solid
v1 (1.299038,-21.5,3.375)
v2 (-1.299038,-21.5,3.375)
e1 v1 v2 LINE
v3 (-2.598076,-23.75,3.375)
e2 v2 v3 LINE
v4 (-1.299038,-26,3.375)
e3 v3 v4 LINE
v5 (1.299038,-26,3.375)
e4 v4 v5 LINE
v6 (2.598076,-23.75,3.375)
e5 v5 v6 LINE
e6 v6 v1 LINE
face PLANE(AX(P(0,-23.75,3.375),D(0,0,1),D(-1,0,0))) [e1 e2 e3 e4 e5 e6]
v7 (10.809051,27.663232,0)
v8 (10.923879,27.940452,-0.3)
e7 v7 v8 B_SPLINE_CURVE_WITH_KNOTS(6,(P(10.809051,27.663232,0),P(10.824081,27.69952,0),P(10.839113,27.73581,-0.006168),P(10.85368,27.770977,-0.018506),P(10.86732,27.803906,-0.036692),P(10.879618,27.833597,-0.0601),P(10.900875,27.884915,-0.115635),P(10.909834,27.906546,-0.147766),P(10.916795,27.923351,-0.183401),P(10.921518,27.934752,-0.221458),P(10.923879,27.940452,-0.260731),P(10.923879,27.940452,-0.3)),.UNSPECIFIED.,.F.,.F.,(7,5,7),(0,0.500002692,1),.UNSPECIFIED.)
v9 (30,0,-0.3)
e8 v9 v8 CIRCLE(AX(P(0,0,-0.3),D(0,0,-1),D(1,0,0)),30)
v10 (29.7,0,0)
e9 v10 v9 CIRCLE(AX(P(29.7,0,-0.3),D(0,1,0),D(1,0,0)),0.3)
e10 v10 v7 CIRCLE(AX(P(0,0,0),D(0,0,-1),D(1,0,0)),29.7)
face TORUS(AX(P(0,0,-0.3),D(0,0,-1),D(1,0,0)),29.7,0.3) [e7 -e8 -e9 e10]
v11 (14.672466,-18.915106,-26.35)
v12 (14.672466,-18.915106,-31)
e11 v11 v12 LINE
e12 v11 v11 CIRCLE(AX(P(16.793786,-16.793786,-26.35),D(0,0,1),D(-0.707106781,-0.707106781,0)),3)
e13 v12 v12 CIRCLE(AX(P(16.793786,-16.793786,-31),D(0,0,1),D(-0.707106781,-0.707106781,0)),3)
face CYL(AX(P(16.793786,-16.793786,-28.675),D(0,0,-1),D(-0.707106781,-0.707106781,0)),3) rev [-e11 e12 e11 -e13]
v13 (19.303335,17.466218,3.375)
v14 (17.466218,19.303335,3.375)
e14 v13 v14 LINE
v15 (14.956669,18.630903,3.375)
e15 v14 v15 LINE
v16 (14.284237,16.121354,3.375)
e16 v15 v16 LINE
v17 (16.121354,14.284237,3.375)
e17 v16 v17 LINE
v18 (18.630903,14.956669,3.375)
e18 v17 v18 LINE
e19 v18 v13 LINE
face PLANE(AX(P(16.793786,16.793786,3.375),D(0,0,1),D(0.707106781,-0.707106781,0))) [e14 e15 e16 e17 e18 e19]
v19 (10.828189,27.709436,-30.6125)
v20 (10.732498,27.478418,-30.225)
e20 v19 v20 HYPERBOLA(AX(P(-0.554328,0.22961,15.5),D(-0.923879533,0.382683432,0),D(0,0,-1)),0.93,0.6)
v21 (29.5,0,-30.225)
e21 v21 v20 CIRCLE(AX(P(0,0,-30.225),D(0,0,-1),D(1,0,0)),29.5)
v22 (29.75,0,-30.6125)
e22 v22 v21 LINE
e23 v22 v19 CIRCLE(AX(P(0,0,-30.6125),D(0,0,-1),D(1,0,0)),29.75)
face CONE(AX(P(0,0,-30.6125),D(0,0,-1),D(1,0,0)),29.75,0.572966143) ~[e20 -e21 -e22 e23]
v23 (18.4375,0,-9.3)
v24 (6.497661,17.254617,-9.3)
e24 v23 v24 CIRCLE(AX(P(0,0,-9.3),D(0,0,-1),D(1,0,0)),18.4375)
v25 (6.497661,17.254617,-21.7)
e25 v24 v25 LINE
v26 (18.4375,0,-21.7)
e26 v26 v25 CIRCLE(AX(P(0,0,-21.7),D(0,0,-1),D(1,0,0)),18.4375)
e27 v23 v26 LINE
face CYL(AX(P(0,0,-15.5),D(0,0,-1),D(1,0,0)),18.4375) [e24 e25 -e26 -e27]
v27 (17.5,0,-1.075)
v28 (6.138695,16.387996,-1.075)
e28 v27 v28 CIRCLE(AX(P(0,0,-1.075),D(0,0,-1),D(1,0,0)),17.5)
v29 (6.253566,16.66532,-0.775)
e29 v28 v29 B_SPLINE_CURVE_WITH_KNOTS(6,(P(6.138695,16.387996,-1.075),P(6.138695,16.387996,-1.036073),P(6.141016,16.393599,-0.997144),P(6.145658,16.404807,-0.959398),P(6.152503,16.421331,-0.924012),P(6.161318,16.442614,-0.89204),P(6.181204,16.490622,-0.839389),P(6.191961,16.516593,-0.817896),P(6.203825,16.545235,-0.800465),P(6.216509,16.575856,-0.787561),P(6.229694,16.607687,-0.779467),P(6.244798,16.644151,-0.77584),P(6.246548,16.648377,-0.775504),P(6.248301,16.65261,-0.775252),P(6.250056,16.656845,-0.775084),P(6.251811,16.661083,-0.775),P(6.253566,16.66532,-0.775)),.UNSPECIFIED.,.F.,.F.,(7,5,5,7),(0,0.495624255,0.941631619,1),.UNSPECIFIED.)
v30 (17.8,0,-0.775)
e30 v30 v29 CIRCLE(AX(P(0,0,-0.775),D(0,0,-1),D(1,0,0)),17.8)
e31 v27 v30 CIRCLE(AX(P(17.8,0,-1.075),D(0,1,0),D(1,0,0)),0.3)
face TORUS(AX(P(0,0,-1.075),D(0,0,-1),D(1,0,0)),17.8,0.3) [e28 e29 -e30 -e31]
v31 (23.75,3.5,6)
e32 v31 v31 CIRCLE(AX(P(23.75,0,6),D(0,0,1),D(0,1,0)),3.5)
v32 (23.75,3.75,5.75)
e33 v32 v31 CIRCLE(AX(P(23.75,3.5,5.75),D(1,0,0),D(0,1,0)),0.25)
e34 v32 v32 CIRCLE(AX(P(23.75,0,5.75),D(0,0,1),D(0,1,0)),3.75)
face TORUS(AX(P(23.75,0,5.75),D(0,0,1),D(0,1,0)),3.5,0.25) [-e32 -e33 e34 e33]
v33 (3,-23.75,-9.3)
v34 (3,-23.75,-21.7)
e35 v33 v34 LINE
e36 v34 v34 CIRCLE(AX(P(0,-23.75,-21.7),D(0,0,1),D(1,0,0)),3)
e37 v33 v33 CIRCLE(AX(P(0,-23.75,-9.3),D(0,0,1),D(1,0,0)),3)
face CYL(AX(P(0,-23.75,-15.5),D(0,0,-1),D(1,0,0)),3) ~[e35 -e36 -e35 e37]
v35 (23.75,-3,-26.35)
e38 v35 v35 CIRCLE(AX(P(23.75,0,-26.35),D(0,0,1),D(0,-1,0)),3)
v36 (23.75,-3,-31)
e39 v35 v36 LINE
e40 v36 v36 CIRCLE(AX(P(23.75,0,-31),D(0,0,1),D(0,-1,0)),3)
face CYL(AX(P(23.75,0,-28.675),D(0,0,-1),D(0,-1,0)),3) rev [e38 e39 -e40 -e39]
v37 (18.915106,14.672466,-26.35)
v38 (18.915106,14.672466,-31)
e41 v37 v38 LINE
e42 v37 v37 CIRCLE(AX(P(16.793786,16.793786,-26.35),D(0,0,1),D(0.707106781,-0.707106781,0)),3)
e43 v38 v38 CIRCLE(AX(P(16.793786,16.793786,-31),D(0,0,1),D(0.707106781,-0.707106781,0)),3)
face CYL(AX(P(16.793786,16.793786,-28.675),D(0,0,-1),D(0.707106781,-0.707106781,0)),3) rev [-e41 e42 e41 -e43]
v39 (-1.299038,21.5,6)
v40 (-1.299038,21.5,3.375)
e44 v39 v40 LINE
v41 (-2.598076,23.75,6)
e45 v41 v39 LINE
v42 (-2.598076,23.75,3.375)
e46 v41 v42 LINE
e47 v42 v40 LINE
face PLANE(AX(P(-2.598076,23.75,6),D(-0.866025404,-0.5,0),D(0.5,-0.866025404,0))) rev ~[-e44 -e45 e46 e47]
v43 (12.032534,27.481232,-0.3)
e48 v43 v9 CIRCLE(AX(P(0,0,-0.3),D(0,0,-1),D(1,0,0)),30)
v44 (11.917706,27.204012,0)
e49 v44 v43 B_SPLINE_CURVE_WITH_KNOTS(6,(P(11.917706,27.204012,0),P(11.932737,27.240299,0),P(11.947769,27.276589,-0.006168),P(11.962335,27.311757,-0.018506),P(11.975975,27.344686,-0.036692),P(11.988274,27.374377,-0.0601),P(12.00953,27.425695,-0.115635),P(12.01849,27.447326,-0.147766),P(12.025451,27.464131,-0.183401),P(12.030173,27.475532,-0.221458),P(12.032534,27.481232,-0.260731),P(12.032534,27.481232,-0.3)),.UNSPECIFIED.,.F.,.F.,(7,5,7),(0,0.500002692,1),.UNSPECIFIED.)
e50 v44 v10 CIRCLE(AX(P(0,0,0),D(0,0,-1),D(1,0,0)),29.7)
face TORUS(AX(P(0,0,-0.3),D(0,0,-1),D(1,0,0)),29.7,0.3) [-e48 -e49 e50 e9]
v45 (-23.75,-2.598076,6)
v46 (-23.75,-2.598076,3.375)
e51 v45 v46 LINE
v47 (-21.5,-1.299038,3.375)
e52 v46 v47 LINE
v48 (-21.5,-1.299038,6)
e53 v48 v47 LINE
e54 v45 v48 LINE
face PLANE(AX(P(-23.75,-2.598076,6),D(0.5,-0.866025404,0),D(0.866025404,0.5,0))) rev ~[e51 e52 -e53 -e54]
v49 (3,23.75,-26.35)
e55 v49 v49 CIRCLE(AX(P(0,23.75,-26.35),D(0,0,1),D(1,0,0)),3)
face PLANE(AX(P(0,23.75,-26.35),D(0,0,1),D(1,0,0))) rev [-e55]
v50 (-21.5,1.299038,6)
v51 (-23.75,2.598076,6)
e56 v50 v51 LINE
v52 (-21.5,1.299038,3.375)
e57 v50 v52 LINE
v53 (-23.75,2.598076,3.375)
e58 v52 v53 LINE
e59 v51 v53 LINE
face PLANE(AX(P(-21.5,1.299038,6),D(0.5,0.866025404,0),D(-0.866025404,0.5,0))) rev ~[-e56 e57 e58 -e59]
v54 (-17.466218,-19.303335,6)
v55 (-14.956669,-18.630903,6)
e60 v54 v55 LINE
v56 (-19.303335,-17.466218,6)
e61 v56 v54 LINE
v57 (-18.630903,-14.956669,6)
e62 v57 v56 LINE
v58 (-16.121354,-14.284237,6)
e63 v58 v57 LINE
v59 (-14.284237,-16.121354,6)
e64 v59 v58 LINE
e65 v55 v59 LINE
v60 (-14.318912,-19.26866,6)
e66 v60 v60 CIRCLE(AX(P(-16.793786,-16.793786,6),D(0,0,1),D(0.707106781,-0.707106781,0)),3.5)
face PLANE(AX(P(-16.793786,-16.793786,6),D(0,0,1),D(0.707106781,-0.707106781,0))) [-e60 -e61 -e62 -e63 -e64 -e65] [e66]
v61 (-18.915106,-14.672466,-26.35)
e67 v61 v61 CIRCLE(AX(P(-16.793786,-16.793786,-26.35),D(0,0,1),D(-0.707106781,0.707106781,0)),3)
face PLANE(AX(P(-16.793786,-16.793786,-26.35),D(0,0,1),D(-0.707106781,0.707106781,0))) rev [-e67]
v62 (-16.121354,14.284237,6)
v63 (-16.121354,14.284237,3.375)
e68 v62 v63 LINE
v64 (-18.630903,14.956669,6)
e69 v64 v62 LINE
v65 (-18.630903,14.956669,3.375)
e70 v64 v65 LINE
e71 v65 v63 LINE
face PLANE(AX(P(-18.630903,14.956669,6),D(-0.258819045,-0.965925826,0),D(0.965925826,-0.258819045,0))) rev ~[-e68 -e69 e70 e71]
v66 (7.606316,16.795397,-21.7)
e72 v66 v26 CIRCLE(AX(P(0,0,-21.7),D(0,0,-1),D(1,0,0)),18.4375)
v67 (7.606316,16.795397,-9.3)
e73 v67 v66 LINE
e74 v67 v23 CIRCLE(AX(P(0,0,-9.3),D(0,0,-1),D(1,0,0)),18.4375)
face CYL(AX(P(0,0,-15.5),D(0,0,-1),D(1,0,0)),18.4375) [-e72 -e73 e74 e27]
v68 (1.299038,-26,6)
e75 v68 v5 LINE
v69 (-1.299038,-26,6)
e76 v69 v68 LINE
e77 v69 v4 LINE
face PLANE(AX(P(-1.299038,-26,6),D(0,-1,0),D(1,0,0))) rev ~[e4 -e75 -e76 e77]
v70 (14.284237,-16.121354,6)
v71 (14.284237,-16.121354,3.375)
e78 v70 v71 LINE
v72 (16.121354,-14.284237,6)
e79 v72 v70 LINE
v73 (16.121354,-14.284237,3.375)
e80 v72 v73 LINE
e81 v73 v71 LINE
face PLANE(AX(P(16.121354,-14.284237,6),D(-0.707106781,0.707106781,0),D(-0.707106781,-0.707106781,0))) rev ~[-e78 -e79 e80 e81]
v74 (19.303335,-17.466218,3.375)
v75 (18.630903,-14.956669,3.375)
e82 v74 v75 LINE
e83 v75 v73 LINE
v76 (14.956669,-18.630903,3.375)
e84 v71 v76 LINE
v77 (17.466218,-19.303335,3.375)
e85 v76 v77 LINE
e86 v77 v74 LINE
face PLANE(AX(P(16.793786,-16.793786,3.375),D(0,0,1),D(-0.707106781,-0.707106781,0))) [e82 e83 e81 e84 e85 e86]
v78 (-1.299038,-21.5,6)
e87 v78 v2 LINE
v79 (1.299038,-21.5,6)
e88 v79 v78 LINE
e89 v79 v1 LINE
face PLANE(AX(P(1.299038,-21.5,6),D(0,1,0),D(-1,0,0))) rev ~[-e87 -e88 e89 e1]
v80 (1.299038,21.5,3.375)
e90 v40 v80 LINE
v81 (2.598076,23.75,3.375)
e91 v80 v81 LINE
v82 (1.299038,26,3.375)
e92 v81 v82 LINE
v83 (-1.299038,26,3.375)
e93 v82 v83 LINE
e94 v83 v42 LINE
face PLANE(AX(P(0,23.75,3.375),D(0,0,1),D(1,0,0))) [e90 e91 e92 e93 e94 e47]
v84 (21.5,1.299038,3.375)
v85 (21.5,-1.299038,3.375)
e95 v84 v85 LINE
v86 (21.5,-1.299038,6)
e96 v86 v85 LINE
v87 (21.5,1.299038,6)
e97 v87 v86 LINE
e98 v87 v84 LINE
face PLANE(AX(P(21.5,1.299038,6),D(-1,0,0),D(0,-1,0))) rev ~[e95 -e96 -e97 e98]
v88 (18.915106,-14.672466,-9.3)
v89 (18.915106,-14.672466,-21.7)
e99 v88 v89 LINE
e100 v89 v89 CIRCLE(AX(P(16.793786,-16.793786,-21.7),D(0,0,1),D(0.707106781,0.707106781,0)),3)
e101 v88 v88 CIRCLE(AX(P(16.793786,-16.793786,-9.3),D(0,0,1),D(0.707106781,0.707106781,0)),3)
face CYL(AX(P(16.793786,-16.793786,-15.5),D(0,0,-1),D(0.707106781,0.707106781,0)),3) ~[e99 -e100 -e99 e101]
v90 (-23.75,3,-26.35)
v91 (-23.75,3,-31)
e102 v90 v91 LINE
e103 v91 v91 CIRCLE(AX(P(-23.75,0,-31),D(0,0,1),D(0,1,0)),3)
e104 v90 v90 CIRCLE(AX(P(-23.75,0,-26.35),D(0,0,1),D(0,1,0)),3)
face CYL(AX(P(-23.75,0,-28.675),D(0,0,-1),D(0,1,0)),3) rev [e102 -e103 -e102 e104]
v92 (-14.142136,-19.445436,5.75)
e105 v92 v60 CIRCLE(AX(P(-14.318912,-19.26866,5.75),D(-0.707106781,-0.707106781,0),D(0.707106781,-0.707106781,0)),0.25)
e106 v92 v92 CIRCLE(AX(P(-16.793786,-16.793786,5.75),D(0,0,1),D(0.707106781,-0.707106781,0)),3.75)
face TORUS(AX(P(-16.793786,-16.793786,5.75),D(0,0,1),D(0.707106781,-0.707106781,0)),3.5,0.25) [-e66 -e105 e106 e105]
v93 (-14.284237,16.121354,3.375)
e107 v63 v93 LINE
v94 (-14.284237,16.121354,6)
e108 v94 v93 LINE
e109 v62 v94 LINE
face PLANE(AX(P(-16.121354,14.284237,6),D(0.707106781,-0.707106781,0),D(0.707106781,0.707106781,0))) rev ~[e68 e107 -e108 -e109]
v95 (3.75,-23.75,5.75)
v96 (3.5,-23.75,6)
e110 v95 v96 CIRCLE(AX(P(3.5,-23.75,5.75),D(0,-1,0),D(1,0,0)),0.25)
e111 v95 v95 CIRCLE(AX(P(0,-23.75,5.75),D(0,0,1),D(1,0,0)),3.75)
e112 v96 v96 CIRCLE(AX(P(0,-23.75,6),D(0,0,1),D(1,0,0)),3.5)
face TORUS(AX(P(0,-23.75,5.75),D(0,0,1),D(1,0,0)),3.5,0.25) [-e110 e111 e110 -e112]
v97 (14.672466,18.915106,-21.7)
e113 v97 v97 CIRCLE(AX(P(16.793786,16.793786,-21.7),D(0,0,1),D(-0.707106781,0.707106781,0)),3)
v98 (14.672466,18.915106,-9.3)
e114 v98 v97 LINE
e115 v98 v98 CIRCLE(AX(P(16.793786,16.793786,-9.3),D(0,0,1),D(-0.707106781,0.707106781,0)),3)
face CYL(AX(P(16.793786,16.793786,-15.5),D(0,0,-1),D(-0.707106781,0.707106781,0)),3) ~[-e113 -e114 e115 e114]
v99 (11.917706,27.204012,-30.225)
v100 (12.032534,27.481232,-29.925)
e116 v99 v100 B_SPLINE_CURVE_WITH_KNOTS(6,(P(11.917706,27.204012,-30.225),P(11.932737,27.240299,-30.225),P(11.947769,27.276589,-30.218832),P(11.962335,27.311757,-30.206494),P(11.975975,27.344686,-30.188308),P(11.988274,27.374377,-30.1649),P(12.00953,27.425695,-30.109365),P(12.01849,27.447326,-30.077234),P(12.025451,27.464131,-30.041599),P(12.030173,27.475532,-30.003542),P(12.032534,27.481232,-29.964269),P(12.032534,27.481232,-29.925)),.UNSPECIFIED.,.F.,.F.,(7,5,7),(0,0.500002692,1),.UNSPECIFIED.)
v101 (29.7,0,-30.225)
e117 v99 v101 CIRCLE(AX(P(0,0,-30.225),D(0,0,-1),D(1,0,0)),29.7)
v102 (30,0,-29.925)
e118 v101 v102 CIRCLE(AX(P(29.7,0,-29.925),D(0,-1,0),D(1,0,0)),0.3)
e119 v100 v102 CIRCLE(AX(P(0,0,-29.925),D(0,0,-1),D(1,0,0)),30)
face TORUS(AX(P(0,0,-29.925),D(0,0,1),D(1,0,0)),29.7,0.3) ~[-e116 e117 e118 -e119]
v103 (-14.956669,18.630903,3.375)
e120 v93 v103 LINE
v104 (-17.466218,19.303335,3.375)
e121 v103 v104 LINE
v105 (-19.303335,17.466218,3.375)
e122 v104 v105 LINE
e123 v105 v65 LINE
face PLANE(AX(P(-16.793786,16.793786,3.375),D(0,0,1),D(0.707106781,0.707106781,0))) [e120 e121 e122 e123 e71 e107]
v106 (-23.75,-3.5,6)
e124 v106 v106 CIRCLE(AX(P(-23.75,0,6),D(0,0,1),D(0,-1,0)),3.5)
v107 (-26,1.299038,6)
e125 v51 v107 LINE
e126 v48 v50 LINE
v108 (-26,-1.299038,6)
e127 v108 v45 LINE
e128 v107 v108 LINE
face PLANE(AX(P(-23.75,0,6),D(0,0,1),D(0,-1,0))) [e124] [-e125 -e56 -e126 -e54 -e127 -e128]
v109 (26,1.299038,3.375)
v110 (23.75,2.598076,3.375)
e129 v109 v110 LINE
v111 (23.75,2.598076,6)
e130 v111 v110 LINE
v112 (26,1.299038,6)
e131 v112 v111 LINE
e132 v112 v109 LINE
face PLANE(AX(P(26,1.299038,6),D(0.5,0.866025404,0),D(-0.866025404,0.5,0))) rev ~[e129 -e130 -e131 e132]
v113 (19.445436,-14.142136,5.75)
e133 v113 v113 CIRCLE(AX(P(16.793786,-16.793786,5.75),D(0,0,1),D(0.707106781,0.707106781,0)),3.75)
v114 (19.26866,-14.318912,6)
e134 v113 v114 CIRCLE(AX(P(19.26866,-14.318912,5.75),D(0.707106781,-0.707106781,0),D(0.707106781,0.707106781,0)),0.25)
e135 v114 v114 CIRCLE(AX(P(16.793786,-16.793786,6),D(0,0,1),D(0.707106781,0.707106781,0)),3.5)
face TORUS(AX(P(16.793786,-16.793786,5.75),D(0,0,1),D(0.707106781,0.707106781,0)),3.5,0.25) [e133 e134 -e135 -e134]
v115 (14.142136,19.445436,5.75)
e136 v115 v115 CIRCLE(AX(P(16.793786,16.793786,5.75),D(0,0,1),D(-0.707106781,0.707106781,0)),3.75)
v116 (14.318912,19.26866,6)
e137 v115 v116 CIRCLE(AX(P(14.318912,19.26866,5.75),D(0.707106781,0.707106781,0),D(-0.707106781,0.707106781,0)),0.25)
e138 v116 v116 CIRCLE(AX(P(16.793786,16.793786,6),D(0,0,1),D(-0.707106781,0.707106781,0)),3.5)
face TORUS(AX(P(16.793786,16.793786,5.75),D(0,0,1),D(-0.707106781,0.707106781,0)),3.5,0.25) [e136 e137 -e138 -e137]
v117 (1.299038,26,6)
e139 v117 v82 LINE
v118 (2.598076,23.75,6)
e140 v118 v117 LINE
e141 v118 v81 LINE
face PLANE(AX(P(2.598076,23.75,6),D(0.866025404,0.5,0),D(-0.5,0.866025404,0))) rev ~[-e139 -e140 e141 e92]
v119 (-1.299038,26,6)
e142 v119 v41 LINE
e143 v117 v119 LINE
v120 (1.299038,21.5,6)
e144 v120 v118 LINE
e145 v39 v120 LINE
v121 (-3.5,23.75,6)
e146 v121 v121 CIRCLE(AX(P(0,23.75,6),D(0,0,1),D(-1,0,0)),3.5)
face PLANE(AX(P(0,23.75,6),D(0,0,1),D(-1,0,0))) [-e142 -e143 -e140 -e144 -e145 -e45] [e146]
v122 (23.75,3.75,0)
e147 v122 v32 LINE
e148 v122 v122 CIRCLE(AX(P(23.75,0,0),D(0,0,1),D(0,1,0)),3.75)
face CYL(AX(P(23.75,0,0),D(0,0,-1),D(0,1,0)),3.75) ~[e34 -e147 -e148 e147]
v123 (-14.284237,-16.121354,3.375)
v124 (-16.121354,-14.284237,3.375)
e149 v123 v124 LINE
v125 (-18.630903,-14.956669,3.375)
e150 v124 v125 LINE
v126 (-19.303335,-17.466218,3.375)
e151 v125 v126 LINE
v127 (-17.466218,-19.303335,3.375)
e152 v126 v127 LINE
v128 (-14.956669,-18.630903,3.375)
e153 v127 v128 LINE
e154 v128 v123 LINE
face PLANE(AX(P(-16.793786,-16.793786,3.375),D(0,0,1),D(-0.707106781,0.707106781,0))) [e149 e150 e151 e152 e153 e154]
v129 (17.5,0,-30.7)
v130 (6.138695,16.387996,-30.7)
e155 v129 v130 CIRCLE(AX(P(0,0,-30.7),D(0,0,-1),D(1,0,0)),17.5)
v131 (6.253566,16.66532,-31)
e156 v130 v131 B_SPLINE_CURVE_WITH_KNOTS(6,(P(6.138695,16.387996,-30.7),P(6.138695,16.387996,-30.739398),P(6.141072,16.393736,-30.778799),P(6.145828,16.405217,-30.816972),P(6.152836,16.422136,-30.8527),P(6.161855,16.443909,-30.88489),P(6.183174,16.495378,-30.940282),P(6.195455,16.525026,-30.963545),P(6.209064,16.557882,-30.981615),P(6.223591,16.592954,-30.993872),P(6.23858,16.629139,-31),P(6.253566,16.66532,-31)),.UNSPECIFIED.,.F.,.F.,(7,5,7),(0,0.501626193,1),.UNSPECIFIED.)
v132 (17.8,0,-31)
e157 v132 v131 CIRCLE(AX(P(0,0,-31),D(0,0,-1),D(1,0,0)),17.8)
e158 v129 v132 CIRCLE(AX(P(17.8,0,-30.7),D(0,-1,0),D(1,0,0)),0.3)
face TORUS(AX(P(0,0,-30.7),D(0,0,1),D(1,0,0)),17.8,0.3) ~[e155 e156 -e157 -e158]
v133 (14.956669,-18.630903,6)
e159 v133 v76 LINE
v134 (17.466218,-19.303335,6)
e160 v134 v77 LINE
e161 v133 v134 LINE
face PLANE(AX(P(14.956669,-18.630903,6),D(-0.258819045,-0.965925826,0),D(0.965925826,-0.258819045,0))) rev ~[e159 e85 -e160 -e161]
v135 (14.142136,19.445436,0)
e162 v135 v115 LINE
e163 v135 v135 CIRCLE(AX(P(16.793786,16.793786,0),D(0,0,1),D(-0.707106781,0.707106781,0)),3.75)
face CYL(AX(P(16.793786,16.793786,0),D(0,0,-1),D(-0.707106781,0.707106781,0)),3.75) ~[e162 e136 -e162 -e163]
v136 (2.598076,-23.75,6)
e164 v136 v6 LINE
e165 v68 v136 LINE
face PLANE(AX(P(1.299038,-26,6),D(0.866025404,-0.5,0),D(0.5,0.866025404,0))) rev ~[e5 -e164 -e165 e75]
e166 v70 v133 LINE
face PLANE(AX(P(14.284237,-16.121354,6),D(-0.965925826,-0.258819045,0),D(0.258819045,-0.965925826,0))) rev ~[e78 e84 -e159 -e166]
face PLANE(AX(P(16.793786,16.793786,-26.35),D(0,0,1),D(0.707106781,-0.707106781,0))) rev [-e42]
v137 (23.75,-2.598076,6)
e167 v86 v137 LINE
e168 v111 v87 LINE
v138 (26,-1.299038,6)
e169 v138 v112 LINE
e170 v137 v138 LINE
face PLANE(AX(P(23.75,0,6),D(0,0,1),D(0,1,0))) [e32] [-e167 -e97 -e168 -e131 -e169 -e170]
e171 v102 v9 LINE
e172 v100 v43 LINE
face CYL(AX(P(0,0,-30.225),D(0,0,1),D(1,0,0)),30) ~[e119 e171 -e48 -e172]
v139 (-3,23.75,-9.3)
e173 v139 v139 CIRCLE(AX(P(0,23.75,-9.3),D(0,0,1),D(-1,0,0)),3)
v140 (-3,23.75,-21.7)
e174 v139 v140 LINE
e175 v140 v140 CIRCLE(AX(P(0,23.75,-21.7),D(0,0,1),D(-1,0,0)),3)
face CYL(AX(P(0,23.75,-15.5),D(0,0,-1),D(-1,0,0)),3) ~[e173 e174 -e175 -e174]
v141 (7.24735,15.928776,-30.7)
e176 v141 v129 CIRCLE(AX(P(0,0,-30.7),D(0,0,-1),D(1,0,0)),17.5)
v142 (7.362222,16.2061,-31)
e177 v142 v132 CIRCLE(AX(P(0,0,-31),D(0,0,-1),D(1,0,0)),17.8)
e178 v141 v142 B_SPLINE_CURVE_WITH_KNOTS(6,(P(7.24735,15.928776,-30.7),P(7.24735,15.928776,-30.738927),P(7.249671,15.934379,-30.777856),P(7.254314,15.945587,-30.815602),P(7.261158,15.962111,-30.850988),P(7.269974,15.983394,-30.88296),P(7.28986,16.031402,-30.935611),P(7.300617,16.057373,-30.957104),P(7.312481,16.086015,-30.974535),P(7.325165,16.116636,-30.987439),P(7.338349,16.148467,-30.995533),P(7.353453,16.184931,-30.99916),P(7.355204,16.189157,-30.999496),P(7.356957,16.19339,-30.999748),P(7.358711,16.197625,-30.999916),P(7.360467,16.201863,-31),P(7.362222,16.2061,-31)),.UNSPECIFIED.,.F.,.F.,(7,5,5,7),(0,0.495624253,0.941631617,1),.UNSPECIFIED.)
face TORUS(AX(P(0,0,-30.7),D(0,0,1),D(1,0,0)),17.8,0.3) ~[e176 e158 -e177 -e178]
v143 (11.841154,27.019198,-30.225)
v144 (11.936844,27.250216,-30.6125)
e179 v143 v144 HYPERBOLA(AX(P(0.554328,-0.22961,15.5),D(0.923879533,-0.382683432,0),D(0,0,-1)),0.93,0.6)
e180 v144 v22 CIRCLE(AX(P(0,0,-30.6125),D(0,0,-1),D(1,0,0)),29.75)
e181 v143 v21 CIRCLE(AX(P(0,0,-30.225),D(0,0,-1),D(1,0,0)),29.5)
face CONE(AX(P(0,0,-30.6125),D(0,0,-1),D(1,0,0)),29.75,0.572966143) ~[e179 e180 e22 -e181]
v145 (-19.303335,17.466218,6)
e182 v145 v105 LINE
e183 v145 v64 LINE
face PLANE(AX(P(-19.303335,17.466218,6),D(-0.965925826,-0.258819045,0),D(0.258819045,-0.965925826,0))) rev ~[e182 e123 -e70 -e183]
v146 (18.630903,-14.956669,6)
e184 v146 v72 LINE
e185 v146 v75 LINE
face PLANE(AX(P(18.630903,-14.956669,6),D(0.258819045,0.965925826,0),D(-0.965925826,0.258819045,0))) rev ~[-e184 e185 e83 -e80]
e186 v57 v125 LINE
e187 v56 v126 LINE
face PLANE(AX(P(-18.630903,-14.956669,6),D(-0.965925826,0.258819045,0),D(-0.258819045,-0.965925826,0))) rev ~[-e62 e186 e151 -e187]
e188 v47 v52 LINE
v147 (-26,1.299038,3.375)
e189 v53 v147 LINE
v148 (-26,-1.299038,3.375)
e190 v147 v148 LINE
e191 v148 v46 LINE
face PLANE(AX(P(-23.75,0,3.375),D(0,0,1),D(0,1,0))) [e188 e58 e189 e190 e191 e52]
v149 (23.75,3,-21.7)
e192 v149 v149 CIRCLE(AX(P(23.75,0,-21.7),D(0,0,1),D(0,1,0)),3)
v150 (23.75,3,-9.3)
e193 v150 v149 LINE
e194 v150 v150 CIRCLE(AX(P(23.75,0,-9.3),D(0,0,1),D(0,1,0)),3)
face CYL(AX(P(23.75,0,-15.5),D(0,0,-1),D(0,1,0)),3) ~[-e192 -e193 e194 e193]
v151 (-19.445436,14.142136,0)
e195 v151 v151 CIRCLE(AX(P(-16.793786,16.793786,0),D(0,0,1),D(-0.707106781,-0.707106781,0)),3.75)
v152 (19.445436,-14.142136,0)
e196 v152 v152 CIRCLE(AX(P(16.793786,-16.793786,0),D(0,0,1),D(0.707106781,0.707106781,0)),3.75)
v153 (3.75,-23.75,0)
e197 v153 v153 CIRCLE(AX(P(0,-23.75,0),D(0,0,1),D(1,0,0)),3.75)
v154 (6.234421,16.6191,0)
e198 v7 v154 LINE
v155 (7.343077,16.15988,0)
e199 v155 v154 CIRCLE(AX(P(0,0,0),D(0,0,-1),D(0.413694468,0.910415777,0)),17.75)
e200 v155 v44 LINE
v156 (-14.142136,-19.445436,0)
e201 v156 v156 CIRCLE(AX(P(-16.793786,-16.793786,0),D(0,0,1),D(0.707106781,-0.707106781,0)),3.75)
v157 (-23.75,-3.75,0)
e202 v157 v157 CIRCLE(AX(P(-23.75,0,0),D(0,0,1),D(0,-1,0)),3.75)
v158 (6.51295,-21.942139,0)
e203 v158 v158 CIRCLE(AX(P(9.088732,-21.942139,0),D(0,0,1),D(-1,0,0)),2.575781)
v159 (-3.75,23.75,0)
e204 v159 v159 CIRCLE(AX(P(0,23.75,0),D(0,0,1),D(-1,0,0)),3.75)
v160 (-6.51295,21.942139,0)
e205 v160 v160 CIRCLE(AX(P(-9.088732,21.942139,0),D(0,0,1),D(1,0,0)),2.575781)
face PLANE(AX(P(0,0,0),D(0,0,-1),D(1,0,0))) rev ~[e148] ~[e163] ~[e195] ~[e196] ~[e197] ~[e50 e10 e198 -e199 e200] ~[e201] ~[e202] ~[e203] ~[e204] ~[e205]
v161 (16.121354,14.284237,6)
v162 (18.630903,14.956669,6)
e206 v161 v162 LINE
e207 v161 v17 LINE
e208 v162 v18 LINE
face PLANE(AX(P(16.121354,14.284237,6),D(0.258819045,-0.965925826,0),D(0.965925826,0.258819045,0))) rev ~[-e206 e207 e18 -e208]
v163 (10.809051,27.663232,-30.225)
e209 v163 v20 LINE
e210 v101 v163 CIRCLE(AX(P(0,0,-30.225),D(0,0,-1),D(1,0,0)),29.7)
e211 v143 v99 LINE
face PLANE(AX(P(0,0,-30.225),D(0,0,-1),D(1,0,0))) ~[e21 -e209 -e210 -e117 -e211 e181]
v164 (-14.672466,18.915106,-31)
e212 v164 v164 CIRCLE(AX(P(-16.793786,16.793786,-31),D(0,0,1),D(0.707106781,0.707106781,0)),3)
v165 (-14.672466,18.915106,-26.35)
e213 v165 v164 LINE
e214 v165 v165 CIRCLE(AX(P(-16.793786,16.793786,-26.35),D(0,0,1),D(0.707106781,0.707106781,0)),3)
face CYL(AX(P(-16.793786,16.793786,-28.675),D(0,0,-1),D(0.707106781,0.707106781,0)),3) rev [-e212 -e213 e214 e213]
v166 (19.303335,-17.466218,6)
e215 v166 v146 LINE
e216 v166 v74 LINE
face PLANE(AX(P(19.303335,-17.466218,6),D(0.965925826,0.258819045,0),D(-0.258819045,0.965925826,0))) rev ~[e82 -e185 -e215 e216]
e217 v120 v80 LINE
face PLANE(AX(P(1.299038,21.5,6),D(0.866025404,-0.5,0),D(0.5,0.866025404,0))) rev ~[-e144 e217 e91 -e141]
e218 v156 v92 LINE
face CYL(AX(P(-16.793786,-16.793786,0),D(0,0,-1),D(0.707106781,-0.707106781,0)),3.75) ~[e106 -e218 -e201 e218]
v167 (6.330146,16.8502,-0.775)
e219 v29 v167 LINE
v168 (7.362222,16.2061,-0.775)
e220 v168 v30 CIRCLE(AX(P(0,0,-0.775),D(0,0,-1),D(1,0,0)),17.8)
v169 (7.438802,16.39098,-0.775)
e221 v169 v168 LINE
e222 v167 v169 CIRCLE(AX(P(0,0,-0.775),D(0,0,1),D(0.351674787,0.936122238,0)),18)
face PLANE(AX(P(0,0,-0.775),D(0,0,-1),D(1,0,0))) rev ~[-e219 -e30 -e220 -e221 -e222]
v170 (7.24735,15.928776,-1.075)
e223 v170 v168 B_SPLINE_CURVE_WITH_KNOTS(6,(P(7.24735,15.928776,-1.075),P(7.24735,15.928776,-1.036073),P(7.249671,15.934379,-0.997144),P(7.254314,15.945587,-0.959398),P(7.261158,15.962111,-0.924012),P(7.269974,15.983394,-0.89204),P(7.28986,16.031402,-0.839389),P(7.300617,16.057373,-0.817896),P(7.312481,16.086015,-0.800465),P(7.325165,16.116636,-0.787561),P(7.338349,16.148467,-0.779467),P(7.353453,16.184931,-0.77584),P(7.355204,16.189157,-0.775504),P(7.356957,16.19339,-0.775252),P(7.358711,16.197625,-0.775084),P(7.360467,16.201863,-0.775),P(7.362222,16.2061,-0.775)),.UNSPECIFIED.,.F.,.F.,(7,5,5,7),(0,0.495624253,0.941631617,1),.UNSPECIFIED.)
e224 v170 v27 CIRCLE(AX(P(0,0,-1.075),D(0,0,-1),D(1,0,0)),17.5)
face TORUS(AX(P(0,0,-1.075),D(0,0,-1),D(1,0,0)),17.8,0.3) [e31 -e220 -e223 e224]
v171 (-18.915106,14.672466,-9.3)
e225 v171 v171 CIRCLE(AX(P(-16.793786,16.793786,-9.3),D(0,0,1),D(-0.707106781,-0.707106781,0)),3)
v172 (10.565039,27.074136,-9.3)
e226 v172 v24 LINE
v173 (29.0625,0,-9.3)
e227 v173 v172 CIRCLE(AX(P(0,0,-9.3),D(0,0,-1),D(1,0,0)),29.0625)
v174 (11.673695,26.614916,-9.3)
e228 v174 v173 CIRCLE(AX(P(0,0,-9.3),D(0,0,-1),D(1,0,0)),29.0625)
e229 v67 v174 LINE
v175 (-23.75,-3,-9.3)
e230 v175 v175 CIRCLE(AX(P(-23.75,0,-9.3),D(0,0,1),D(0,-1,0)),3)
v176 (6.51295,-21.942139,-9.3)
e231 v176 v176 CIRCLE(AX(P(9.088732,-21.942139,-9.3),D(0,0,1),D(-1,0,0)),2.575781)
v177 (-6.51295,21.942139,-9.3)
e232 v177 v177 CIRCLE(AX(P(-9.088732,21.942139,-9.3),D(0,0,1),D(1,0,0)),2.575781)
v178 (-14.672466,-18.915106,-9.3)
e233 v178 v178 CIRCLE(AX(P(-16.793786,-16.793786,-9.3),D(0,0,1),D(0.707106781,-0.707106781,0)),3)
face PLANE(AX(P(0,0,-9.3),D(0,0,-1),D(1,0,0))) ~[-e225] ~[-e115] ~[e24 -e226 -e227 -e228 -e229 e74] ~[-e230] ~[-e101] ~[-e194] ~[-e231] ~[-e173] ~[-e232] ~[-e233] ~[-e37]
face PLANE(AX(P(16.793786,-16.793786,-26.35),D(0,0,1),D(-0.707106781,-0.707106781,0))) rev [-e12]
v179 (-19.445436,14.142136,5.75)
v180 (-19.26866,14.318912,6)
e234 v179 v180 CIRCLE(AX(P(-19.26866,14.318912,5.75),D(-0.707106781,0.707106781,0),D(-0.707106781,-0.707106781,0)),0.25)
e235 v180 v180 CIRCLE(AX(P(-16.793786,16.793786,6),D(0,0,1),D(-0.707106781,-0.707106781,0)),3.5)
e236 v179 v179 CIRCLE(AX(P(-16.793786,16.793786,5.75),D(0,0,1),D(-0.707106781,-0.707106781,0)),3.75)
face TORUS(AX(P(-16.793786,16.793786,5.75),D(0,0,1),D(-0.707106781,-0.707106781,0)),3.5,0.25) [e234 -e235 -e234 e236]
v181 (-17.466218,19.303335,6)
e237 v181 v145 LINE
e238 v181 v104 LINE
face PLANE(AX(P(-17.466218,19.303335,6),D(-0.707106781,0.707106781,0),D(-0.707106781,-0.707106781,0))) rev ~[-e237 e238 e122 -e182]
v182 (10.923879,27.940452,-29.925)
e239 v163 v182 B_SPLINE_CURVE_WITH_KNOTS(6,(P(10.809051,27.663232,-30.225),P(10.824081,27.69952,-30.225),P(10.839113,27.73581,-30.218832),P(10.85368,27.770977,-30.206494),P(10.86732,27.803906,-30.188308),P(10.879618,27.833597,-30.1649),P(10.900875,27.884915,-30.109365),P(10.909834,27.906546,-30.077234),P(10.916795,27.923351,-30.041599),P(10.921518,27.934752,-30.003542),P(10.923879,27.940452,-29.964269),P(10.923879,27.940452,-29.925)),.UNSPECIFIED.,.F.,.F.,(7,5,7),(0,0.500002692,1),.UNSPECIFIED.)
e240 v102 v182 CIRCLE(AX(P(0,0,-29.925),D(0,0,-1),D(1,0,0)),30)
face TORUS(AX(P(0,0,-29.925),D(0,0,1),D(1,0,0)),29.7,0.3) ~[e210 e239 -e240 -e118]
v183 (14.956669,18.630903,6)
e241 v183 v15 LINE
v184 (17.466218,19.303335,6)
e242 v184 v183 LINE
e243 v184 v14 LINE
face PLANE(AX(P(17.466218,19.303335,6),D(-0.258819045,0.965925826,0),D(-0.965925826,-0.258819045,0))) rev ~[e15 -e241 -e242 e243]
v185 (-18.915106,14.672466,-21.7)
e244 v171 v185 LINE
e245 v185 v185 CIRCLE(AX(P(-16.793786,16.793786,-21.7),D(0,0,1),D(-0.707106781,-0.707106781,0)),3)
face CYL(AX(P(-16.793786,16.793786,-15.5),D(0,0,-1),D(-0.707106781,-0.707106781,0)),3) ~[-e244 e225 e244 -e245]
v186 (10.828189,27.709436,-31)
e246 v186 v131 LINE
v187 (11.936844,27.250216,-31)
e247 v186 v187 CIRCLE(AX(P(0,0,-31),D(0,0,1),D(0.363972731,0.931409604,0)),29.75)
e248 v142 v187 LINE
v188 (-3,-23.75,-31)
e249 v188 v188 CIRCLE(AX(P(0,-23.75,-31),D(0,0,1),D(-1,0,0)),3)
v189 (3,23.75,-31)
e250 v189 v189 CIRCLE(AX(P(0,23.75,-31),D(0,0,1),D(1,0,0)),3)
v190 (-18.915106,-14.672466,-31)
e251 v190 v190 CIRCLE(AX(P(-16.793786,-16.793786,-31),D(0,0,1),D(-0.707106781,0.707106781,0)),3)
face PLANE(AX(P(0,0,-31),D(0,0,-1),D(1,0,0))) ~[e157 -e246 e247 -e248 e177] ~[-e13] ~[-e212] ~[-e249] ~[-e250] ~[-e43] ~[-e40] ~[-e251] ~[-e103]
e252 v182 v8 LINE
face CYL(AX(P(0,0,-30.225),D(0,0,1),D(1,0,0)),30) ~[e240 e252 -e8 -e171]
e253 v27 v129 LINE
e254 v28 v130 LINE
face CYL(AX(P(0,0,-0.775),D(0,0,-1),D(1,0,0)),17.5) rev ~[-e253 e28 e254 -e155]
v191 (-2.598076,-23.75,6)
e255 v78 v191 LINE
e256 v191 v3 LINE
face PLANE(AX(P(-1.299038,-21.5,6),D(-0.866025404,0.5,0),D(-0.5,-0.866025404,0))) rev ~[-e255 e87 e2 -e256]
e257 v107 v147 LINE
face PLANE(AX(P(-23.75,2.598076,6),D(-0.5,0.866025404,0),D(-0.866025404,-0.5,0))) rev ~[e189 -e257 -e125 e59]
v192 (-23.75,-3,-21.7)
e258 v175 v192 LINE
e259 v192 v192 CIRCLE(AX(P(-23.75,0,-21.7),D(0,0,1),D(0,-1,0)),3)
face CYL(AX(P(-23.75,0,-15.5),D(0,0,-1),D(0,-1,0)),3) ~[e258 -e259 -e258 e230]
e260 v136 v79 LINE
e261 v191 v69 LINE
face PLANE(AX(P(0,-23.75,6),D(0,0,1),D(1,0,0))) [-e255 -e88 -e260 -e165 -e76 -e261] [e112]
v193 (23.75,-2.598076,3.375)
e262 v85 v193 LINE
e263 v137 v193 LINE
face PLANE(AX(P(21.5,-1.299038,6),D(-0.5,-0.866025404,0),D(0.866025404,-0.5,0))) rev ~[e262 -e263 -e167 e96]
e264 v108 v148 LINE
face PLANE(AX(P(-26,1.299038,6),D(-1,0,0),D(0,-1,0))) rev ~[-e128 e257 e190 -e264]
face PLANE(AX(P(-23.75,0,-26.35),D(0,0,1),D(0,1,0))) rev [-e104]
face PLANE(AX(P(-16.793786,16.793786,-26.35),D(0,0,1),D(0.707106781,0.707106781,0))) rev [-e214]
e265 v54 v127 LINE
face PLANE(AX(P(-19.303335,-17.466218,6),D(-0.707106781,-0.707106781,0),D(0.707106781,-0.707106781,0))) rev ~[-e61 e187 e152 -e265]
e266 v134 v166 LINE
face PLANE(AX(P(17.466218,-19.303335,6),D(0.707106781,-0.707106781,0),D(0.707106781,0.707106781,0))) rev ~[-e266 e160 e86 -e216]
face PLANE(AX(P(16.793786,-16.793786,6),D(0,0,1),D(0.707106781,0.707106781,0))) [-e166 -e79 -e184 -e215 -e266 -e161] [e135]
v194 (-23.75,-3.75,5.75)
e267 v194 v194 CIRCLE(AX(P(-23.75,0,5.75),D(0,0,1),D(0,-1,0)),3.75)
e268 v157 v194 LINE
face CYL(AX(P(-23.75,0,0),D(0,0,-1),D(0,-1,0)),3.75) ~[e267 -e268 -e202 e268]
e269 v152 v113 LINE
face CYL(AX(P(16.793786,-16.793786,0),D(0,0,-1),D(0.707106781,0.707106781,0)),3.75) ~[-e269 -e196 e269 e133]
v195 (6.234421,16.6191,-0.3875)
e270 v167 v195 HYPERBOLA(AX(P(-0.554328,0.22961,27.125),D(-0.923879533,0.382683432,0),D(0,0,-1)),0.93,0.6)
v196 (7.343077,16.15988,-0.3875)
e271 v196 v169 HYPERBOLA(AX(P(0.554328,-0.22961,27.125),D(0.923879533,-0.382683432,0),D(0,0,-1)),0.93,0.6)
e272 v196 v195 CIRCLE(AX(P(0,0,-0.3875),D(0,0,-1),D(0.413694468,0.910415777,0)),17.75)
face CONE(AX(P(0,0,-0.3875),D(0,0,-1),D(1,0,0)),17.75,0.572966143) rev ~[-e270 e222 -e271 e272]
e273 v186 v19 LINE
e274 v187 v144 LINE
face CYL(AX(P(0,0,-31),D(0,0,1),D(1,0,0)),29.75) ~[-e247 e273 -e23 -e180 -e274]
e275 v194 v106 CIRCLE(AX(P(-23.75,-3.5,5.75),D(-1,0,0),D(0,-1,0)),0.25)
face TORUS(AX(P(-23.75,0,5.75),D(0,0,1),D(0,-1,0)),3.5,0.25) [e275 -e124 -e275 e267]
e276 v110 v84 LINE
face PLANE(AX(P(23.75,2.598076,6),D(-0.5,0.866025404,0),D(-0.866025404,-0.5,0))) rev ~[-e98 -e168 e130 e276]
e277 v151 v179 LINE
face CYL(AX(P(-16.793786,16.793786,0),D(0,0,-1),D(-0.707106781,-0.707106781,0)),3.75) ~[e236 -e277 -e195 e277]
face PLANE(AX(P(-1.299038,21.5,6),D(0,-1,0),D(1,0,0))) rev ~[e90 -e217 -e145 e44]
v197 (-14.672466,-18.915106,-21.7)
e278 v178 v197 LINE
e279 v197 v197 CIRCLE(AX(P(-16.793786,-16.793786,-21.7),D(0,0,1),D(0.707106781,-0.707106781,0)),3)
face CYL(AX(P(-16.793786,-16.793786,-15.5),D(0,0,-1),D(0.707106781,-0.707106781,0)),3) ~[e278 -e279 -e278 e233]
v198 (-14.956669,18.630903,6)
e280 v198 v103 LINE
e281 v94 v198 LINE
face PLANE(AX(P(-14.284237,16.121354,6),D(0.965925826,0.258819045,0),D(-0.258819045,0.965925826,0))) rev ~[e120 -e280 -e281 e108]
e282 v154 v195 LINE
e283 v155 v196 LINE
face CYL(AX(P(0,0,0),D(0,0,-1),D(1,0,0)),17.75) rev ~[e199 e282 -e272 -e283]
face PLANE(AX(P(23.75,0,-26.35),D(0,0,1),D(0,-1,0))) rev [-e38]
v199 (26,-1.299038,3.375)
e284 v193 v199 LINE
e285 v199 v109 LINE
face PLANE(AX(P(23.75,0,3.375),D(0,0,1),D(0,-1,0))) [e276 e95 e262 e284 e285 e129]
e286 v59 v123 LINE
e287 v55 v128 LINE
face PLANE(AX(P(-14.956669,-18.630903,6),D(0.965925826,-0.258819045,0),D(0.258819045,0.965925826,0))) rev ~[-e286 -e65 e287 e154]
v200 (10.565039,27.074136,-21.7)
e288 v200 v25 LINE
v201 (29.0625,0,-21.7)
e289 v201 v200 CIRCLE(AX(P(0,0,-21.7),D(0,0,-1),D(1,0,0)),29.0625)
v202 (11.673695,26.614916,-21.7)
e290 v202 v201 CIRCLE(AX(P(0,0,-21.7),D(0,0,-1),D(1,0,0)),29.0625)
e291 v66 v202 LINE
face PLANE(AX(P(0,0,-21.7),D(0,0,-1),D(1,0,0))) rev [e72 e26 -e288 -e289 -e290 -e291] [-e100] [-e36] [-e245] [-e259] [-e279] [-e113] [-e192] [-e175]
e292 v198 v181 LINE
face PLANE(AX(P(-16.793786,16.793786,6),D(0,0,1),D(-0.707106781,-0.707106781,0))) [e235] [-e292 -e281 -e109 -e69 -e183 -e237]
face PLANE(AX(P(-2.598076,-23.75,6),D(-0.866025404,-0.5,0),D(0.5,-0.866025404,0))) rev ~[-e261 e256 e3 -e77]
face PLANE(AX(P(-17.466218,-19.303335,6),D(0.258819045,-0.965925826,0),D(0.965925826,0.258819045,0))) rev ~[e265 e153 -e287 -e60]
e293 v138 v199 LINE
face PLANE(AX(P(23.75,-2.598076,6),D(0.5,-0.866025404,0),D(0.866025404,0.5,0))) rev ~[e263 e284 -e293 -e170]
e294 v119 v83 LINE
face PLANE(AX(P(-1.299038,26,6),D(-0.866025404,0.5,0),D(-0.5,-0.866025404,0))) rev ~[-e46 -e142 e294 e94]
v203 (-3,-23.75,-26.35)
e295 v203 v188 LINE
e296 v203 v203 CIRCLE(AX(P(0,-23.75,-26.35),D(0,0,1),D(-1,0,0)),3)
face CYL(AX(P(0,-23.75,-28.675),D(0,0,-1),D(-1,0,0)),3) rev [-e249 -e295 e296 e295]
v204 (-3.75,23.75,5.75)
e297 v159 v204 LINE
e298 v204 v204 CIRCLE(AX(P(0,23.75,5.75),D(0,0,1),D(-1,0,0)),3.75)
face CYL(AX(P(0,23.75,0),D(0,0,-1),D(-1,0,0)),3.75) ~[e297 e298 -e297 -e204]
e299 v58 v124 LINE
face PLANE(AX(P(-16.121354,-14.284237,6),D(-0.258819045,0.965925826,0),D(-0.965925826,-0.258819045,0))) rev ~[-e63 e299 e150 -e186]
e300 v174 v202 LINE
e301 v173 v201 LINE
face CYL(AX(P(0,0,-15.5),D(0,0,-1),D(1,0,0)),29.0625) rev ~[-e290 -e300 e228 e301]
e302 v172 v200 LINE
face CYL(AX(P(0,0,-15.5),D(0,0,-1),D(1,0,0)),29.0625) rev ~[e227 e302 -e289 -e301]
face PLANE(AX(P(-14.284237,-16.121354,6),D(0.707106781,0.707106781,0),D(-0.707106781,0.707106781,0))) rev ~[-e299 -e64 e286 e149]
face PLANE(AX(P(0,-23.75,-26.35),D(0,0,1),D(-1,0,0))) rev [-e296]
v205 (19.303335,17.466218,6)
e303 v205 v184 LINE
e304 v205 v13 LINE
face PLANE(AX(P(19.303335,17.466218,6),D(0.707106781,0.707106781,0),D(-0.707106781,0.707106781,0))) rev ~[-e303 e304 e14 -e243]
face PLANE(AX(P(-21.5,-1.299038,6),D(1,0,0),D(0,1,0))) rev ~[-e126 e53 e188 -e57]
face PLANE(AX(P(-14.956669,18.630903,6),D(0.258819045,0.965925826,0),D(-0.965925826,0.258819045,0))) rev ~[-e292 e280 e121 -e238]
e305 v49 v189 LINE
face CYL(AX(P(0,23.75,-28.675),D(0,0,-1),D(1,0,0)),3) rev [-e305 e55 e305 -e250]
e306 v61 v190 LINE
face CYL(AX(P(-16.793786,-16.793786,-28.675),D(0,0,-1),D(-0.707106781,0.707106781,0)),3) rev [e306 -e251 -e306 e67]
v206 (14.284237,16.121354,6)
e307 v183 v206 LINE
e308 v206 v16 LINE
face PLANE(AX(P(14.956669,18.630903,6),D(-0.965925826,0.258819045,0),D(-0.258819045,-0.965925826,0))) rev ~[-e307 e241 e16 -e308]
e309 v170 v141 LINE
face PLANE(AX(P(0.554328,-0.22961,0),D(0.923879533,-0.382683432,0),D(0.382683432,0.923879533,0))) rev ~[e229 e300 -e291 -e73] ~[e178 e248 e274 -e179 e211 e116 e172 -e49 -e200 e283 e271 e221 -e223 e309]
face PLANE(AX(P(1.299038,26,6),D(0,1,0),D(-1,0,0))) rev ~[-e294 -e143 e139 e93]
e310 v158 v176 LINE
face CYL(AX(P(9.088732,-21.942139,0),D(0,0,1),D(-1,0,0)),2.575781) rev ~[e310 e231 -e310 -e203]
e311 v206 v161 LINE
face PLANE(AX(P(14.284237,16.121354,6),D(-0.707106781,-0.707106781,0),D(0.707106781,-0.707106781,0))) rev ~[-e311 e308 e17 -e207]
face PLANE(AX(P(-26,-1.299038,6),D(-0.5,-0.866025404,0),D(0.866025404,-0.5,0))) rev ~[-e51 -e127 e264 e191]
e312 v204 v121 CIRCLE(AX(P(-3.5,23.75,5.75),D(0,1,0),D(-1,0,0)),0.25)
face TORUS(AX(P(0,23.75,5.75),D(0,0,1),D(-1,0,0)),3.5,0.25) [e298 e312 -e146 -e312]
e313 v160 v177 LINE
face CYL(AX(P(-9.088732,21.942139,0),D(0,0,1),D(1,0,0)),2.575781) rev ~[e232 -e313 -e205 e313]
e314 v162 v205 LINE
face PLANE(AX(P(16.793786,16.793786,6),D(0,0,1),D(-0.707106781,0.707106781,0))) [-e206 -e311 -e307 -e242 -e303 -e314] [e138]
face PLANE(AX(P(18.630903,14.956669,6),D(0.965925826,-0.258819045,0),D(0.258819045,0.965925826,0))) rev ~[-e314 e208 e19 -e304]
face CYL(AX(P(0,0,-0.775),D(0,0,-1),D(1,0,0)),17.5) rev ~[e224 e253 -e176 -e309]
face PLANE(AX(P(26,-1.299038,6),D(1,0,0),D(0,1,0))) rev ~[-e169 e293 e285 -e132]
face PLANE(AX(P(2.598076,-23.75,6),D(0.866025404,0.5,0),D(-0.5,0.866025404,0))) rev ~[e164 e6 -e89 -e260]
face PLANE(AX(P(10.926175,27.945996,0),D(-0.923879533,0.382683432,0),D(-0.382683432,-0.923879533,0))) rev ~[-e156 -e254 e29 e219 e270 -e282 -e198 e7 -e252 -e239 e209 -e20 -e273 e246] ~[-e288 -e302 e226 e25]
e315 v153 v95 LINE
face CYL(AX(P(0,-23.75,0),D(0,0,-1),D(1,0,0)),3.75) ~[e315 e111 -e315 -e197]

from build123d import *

# Parameters (mm, degrees)
SKETCH7_W                                 = 12.4
SKETCH7_H                                 = 10.625
FILLET2_R                                 = 0.3
SKETCH8_W                                 = 12.4
SKETCH8_H                                 = 3
SCREW_SKETCH1_R                           = 3.75
EXTRUDE_SCREW_SOCKET_HEAD_DEPTH           = 6
FILLET_SCREW_SOCKET_HEAD_R                = 0.25
CUT_SCREW_SOCKET_HEAD_DEPTH               = 2.625
SKETCH5_W                                 = 4.65
SKETCH5_H                                 = 3
CIRPATTERN1_COUNT                         = 8
FILLET_SCREW_SOCKET_HEAD_OF_CIRPATTERN1_R = 0.25
SKETCH6_R                                 = 2.57578125
CUT_EXTRUDE1_DEPTH                        = 9.3
CIRPATTERN2_COUNT                         = 2
CUT_EXTRUDE_THIN1_DEPTH                   = 53.545218679


with BuildPart() as part:
    # Sketch2 → Revolve1 (revolve)
    with BuildSketch(Plane(origin=(0, 0, 0), x_dir=(0, 0, -1), z_dir=(1, 0, 0)), mode=Mode.PRIVATE) as revolve1_sk:
        Polygon((0.775, 17.5), (31, 17.5), (31, 29.75), (30.6125, 29.75), (30.225, 29.5), (30.225, 30), (0, 30), (0, 18), (0, 17.75), (0.3875, 17.75), (0.775, 18), align=None)
    revolve(revolve1_sk.sketch.rotate(Axis((0, 0, 0), (0, 0, -1)), 90), axis=Axis((0, 0, 0), (0, 0, -1)))

    # Sketch7 → Cut-Revolve2 (revolve, cut)
    with BuildSketch(Plane(origin=(0, 0, 0), x_dir=(0, 0, -1), z_dir=(1, 0, 0)), mode=Mode.PRIVATE) as cut_revolve2_sk:
        with Locations((15.5, 23.75)):
            Rectangle(SKETCH7_W, SKETCH7_H)
    revolve(cut_revolve2_sk.sketch.rotate(Axis((0, 0, 0), (0, 0, -1)), 90), axis=Axis((0, 0, 0), (0, 0, -1)), mode=Mode.SUBTRACT)

    # Fillet2
    fillet2_edges = [part.edges().sort_by_distance(p)[0] for p in [
        (-30, 0, 0),
        (-30, 0, -30.225),
        (-17.5, 0, -31),
        (-17.5, 0, -0.775),
    ]]
    fillet(fillet2_edges, radius=FILLET2_R)

    # Sketch8 → Revolve2 (revolve)
    with BuildSketch(Plane(origin=(0, 0, 0), x_dir=(0, 0, -1), z_dir=(1, 0, 0)), mode=Mode.PRIVATE) as revolve2_sk:
        with Locations((15.5, 25.25)):
            Rectangle(SKETCH8_W, SKETCH8_H)
    revolve2 = revolve(revolve2_sk.sketch.rotate(Axis((0, 23.75, -21.7), (0, 0, 1)), 90), axis=Axis((0, 23.75, -21.7), (0, 0, 1)))

    # Screw Sketch1 → Extrude-Screw (socket head) (add)
    with BuildSketch(Plane(origin=(-37.043082829, 76.082538144, 0), x_dir=(1, 0, 0), z_dir=(0, 0, 1))):
        with Locations(Location((37.043082829, -52.332538144, 0), (0, 0, 180))):
            Circle(SCREW_SKETCH1_R)
    extrude_screw_socket_head = extrude(amount=EXTRUDE_SCREW_SOCKET_HEAD_DEPTH)

    # Fillet-Screw (socket head)
    fillet_screw_socket_head_edges = [part.edges().sort_by_distance(p)[0] for p in [
        (3.75, 23.75, 6),
    ]]
    fillet(fillet_screw_socket_head_edges, radius=FILLET_SCREW_SOCKET_HEAD_R)

    # Screw Sketch2 → Cut-Screw (socket head) (cut)
    with BuildSketch(Plane(origin=(0, 82.5, 6), x_dir=(1, 0, 0), z_dir=(0, 0, 1))):
        Polygon((2.598076211, -58.75), (1.299038106, -56.5), (-1.299038106, -56.5), (-2.598076211, -58.75), (-1.299038106, -61), (1.299038106, -61), align=None)
    cut_screw_socket_head = extrude(amount=-CUT_SCREW_SOCKET_HEAD_DEPTH, mode=Mode.SUBTRACT)

    # Sketch5 → Cut-Revolve1 (revolve, cut)
    with BuildSketch(Plane(origin=(0, 0, 0), x_dir=(0, 0, -1), z_dir=(1, 0, 0)), mode=Mode.PRIVATE) as cut_revolve1_sk:
        with Locations((28.675, 25.25)):
            Rectangle(SKETCH5_W, SKETCH5_H)
    cut_revolve1 = revolve(cut_revolve1_sk.sketch.rotate(Axis((0, 23.75, -31), (0, 0, 1)), 270), axis=Axis((0, 23.75, -31), (0, 0, 1)), mode=Mode.SUBTRACT)

    # CirPattern1: Revolve2, Extrude-Screw (socket head), Cut-Screw (socket head), Cut-Revolve1 ×8 about axis
    cirpattern1_axis = Axis((0, 0, 0), (0, 0, 1))
    add([revolve2.rotate(cirpattern1_axis, i * 360 / CIRPATTERN1_COUNT) for i in range(1, CIRPATTERN1_COUNT)])
    add([extrude_screw_socket_head.rotate(cirpattern1_axis, i * 360 / CIRPATTERN1_COUNT) for i in range(1, CIRPATTERN1_COUNT)])
    add([cut_screw_socket_head.rotate(cirpattern1_axis, i * 360 / CIRPATTERN1_COUNT) for i in range(1, CIRPATTERN1_COUNT)], mode=Mode.SUBTRACT)
    add([cut_revolve1.rotate(cirpattern1_axis, i * 360 / CIRPATTERN1_COUNT) for i in range(1, CIRPATTERN1_COUNT)], mode=Mode.SUBTRACT)

    # Fillet-Screw (socket head) of CirPattern1
    fillet_screw_socket_head_of_cirpattern1_edges = [part.edges().sort_by_distance(p)[0] for p in [
        (-14.142135624, 19.445436483, 6),
        (-23.75, 3.75, 6),
        (-19.445436483, -14.142135624, 6),
        (-3.75, -23.75, 6),
        (14.142135624, -19.445436483, 6),
        (23.75, -3.75, 6),
        (19.445436483, 14.142135624, 6),
    ]]
    fillet(fillet_screw_socket_head_of_cirpattern1_edges, radius=FILLET_SCREW_SOCKET_HEAD_OF_CIRPATTERN1_R)

    # Sketch6 → Cut-Extrude1 (cut)
    with BuildSketch(Plane.XY):
        with Locations((-9.088731519, 21.942138897)):
            Circle(SKETCH6_R)
    cut_extrude1 = extrude(amount=-CUT_EXTRUDE1_DEPTH, mode=Mode.SUBTRACT)

    # CirPattern2: Cut-Extrude1 ×2 about axis
    cirpattern2_axis = Axis((0, 0, 0), (0, 0, 1))
    for i in range(1, CIRPATTERN2_COUNT):
        add(cut_extrude1.rotate(cirpattern2_axis, i * 360 / CIRPATTERN2_COUNT), mode=Mode.SUBTRACT)

    # Sketch9 → Cut-Extrude-Thin1 (cut, through all)
    with BuildSketch(Plane.XY):
        Polygon((0.55432772, -0.229610059), (12.03483069, 27.486775916), (10.926175251, 27.945996035), (-0.55432772, 0.229610059), align=None)
    extrude(amount=-CUT_EXTRUDE_THIN1_DEPTH, mode=Mode.SUBTRACT)


solid = part.part
